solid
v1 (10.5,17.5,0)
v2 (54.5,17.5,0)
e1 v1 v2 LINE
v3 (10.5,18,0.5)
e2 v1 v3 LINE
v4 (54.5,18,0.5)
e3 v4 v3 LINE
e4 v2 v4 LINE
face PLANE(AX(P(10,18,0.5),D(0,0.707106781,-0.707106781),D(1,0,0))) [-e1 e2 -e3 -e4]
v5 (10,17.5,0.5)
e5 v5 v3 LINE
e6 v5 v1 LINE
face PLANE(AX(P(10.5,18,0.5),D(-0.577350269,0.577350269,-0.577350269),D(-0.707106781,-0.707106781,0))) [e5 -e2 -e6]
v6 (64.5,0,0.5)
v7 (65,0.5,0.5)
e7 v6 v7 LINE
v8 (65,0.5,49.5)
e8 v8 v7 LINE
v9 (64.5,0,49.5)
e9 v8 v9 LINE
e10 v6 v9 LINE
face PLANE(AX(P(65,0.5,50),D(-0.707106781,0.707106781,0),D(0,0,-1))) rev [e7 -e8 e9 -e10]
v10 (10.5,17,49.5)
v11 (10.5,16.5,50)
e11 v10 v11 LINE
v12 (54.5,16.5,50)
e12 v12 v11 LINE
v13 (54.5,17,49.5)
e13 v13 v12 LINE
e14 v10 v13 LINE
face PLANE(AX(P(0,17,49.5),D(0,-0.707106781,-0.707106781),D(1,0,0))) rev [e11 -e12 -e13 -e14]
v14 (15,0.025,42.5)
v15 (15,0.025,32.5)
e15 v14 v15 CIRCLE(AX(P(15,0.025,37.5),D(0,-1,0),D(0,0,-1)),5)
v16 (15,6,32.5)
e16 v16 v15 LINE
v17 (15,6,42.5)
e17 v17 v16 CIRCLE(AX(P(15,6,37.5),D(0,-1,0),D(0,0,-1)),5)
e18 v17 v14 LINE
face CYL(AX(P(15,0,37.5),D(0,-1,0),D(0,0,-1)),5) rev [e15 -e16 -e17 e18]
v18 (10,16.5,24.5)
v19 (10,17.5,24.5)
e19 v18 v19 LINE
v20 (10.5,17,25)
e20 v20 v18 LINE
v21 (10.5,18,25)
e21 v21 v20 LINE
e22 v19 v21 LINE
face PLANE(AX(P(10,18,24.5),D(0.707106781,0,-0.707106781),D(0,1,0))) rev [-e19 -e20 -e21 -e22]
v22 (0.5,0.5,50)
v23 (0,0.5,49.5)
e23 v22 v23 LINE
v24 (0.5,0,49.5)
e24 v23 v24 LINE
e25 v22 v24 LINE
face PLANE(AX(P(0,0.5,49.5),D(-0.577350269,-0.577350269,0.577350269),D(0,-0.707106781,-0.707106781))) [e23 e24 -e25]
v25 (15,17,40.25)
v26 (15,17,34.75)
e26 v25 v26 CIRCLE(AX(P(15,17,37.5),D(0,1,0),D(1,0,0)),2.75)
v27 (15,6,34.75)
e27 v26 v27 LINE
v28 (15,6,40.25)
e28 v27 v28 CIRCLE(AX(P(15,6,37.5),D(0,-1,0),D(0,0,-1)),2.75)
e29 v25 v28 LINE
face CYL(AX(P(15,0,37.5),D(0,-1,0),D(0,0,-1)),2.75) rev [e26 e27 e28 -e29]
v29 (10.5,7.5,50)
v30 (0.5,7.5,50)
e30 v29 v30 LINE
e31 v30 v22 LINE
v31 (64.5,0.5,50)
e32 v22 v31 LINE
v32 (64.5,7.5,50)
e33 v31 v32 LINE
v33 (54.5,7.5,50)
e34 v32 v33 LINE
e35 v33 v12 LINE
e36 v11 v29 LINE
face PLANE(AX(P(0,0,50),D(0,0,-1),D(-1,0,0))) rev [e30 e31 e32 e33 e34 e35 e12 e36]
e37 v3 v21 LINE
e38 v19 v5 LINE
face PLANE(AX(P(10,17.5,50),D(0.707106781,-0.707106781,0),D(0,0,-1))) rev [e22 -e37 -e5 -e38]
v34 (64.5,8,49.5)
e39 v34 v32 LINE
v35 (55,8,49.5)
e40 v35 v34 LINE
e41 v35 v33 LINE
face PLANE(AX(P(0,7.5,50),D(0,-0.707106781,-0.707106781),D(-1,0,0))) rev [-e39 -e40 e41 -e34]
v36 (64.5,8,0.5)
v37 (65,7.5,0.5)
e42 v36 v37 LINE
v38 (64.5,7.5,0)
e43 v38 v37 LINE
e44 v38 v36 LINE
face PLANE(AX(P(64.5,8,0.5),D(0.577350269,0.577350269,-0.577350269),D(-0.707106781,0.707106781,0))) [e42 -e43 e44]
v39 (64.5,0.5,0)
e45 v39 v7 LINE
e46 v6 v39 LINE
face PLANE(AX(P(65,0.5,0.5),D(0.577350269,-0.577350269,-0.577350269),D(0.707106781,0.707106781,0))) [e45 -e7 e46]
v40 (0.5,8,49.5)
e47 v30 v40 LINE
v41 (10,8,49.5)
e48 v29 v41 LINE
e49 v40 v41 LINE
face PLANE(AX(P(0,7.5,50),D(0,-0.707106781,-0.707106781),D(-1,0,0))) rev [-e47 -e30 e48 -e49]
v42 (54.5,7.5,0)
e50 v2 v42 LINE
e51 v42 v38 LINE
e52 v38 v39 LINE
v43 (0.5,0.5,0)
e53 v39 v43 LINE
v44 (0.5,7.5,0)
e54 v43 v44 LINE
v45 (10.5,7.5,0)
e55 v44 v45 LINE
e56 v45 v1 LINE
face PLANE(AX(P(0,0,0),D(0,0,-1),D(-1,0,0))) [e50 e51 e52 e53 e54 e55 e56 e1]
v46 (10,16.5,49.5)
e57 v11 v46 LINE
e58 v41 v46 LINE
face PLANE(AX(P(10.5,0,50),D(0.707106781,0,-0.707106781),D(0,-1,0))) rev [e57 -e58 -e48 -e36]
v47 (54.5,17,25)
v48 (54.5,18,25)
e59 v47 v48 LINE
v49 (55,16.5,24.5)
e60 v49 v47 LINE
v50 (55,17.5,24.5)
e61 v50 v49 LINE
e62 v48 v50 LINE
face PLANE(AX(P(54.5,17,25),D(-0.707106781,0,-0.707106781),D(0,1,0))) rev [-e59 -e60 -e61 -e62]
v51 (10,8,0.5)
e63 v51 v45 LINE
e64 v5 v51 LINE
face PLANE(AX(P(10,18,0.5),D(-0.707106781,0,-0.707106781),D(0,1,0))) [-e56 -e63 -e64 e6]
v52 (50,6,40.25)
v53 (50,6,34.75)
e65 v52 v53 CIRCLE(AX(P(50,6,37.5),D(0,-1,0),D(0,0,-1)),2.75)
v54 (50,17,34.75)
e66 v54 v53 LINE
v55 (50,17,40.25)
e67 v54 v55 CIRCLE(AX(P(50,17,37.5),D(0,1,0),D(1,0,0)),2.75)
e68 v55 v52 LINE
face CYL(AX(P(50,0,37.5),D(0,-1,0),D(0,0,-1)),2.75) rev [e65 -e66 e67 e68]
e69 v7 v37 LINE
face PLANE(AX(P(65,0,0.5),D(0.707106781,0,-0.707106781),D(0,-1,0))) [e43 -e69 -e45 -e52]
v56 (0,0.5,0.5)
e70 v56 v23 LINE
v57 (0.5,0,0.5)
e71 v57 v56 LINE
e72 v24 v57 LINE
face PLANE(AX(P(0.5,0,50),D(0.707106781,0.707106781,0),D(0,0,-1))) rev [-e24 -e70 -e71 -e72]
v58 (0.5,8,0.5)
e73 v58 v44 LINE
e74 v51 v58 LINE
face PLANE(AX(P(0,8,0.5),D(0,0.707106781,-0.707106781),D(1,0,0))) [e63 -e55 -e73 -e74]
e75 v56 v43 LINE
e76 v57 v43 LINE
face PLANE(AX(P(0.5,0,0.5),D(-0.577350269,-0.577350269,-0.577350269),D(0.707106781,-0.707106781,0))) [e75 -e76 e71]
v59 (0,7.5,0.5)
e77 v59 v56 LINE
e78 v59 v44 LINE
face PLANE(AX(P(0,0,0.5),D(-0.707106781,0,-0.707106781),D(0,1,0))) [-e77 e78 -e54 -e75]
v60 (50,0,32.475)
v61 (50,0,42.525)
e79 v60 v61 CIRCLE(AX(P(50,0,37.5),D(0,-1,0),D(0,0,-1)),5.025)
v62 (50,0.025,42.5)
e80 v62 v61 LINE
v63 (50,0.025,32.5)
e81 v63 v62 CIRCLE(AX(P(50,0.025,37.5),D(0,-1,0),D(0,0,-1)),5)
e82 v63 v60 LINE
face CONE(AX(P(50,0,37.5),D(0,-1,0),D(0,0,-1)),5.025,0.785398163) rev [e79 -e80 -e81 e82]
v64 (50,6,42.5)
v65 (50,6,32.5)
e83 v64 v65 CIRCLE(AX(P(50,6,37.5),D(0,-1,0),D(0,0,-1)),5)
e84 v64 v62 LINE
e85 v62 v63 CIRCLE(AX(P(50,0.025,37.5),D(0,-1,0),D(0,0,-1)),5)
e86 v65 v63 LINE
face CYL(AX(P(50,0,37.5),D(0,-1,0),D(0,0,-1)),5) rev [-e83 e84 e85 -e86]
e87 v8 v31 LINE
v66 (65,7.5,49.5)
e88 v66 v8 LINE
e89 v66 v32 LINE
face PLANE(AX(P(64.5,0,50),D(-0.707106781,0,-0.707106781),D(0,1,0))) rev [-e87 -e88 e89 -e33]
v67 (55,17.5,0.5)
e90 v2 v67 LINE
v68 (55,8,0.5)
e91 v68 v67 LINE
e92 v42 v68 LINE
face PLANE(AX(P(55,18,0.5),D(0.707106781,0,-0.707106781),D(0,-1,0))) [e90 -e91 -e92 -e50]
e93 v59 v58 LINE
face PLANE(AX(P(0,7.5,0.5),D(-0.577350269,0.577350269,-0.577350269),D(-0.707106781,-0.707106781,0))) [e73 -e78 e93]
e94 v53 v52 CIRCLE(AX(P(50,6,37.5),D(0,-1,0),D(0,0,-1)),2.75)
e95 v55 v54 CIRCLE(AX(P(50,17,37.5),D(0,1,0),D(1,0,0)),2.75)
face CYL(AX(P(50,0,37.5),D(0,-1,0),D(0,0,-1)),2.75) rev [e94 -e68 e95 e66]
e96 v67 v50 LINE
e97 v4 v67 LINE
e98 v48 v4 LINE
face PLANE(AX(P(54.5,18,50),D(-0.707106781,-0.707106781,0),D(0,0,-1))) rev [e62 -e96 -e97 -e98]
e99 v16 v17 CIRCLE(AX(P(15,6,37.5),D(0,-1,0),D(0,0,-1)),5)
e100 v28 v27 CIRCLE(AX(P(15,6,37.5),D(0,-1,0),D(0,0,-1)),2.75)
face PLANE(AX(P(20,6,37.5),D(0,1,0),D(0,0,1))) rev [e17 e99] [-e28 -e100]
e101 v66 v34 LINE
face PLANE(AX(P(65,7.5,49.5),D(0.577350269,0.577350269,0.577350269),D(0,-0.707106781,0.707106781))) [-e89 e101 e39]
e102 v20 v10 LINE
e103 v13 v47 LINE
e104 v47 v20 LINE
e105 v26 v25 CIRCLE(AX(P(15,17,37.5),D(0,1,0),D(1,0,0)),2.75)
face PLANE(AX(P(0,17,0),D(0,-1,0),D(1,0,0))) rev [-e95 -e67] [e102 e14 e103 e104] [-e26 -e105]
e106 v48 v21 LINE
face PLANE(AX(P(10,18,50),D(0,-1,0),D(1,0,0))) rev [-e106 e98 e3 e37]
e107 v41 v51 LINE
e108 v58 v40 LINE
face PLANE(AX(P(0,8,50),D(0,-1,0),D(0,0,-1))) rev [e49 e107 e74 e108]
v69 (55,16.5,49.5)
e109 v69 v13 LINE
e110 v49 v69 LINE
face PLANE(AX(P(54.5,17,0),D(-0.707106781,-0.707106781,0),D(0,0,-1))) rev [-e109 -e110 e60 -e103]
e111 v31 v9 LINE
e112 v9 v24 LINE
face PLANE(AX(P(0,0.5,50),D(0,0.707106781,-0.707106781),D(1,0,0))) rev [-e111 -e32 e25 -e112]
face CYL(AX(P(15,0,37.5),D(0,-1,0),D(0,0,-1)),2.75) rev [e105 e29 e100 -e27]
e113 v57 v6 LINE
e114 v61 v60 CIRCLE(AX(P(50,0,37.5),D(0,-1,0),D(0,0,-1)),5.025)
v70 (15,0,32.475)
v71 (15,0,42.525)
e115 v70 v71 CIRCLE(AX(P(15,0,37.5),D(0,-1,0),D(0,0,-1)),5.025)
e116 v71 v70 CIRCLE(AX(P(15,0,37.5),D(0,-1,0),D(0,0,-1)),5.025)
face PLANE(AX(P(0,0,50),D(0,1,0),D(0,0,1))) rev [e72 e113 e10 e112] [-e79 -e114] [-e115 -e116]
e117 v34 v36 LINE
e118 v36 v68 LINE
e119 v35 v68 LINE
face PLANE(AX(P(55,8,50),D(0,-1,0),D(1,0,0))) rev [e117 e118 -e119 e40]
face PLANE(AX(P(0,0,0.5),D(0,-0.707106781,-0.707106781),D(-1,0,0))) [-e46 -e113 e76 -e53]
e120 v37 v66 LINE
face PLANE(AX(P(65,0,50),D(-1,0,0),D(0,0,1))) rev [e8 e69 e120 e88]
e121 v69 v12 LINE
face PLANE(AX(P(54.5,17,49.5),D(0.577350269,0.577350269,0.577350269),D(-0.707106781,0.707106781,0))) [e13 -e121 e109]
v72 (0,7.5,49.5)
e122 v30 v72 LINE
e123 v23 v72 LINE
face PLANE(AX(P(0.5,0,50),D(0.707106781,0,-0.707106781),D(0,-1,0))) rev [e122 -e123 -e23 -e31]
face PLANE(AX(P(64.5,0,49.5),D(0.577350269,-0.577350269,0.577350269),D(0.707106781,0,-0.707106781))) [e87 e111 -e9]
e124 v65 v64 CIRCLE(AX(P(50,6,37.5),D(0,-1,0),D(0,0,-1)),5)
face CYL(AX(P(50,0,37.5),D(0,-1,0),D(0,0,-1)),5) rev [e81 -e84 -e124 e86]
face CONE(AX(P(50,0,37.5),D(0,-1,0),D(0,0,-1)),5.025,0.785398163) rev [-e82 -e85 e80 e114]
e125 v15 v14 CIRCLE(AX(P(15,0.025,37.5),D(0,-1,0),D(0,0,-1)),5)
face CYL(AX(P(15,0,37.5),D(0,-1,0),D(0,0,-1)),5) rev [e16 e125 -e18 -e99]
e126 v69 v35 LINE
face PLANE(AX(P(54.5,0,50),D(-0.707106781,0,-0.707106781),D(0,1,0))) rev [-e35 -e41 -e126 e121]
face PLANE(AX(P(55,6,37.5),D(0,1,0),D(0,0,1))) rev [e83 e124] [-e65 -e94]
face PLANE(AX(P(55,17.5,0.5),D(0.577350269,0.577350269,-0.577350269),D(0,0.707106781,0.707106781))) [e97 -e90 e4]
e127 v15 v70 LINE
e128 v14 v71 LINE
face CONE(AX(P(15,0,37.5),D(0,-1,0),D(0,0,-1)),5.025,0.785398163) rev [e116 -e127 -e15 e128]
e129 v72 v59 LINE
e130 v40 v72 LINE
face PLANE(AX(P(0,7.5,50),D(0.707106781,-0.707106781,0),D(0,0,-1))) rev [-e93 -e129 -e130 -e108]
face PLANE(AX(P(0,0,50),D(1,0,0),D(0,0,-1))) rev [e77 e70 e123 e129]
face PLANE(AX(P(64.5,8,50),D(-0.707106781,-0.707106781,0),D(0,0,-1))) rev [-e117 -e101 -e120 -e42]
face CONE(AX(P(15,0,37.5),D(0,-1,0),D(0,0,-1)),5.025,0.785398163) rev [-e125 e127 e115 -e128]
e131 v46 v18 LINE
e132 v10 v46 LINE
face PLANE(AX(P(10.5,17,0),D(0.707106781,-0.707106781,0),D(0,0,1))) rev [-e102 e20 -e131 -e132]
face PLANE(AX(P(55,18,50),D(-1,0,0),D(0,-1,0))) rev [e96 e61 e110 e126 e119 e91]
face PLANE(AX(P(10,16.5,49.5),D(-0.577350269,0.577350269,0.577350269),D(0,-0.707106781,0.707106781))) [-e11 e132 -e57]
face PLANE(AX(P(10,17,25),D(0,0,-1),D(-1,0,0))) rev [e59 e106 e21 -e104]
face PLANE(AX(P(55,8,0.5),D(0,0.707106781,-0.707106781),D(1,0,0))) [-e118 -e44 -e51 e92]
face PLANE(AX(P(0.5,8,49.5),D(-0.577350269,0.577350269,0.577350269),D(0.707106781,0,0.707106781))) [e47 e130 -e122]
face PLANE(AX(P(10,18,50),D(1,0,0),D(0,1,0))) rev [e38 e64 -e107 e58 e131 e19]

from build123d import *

# Parameters (mm, degrees)
BOSS_EXTRUDE1_DEPTH                          = 50
CBORE_FOR_M5_SLOTTED_CHEESE_HEAD_SCR_2_COUNT = 2
CBORE_FOR_M5_SLOTTED_CHEESE_HEAD_SCR_2_PITCH = 35
SKETCH6_W                                    = 45
SKETCH6_H                                    = 25
CUT_EXTRUDE1_DEPTH                           = 1
CHAMFER1_SIZE                                = 0.5


with BuildPart() as part:
    # Sketch2 → Boss-Extrude1 (new body)
    with BuildSketch(Plane.XY):
        Polygon((55, 8), (65, 8), (65, 0), (0, 0), (0, 8), (10, 8), (10, 18), (55, 18), align=None)
    extrude(amount=BOSS_EXTRUDE1_DEPTH)

    # Sketch4 → CBORE for M5 Slotted cheese head screws1 (revolve, cut)
    with BuildSketch(Plane(origin=(15, 0, 37.5), x_dir=(0, 0, -1), z_dir=(1, 0, 0))):
        Polygon((0, 0), (0, 18), (2.75, 18), (2.75, 6), (5, 6), (5, 0.025), (5.025, 0), align=None)
    cbore_for_m5_slotted_cheese_head_screws1 = revolve(axis=Axis((15, -6.35, 37.5), (0, 1, 0)), mode=Mode.SUBTRACT)

    # CBORE for M5 Slotted cheese head scr 2: CBORE for M5 Slotted cheese head screws1 ×2
    with Locations(*[(i * CBORE_FOR_M5_SLOTTED_CHEESE_HEAD_SCR_2_PITCH, 0, 0) for i in range(1, CBORE_FOR_M5_SLOTTED_CHEESE_HEAD_SCR_2_COUNT)]):
        add(cbore_for_m5_slotted_cheese_head_screws1, mode=Mode.SUBTRACT)

    # Sketch6 → Cut-Extrude1 (cut)
    with BuildSketch(Plane(origin=(0, 18, 0), x_dir=(1, 0, 0), z_dir=(0, 1, 0))):
        with Locations((32.5, -37.5)):
            Rectangle(SKETCH6_W, SKETCH6_H)
    extrude(amount=-CUT_EXTRUDE1_DEPTH, mode=Mode.SUBTRACT)

    # Chamfer1
    chamfer1_edges = [part.edges().sort_by_distance(p)[0] for p in [
        (60, 8, 0),
        (65, 4, 0),
        (32.5, 0, 0),
        (0, 4, 0),
        (65, 4, 50),
        (0, 8, 25),
        (65, 8, 25),
        (65, 0, 25),
        (0, 0, 25),
        (60, 8, 50),
        (55, 12.5, 50),
        (5, 8, 50),
        (10, 12.5, 50),
        (10, 18, 12.5),
        (55, 18, 12.5),
        (0, 4, 50),
        (10, 17, 37.5),
        (10, 17.5, 25),
        (55, 17, 37.5),
        (55, 17.5, 25),
        (32.5, 17, 50),
        (5, 8, 0),
        (32.5, 0, 50),
        (10, 13, 0),
        (32.5, 18, 0),
        (55, 13, 0),
    ]]
    chamfer(chamfer1_edges, length=CHAMFER1_SIZE)


solid = part.part
